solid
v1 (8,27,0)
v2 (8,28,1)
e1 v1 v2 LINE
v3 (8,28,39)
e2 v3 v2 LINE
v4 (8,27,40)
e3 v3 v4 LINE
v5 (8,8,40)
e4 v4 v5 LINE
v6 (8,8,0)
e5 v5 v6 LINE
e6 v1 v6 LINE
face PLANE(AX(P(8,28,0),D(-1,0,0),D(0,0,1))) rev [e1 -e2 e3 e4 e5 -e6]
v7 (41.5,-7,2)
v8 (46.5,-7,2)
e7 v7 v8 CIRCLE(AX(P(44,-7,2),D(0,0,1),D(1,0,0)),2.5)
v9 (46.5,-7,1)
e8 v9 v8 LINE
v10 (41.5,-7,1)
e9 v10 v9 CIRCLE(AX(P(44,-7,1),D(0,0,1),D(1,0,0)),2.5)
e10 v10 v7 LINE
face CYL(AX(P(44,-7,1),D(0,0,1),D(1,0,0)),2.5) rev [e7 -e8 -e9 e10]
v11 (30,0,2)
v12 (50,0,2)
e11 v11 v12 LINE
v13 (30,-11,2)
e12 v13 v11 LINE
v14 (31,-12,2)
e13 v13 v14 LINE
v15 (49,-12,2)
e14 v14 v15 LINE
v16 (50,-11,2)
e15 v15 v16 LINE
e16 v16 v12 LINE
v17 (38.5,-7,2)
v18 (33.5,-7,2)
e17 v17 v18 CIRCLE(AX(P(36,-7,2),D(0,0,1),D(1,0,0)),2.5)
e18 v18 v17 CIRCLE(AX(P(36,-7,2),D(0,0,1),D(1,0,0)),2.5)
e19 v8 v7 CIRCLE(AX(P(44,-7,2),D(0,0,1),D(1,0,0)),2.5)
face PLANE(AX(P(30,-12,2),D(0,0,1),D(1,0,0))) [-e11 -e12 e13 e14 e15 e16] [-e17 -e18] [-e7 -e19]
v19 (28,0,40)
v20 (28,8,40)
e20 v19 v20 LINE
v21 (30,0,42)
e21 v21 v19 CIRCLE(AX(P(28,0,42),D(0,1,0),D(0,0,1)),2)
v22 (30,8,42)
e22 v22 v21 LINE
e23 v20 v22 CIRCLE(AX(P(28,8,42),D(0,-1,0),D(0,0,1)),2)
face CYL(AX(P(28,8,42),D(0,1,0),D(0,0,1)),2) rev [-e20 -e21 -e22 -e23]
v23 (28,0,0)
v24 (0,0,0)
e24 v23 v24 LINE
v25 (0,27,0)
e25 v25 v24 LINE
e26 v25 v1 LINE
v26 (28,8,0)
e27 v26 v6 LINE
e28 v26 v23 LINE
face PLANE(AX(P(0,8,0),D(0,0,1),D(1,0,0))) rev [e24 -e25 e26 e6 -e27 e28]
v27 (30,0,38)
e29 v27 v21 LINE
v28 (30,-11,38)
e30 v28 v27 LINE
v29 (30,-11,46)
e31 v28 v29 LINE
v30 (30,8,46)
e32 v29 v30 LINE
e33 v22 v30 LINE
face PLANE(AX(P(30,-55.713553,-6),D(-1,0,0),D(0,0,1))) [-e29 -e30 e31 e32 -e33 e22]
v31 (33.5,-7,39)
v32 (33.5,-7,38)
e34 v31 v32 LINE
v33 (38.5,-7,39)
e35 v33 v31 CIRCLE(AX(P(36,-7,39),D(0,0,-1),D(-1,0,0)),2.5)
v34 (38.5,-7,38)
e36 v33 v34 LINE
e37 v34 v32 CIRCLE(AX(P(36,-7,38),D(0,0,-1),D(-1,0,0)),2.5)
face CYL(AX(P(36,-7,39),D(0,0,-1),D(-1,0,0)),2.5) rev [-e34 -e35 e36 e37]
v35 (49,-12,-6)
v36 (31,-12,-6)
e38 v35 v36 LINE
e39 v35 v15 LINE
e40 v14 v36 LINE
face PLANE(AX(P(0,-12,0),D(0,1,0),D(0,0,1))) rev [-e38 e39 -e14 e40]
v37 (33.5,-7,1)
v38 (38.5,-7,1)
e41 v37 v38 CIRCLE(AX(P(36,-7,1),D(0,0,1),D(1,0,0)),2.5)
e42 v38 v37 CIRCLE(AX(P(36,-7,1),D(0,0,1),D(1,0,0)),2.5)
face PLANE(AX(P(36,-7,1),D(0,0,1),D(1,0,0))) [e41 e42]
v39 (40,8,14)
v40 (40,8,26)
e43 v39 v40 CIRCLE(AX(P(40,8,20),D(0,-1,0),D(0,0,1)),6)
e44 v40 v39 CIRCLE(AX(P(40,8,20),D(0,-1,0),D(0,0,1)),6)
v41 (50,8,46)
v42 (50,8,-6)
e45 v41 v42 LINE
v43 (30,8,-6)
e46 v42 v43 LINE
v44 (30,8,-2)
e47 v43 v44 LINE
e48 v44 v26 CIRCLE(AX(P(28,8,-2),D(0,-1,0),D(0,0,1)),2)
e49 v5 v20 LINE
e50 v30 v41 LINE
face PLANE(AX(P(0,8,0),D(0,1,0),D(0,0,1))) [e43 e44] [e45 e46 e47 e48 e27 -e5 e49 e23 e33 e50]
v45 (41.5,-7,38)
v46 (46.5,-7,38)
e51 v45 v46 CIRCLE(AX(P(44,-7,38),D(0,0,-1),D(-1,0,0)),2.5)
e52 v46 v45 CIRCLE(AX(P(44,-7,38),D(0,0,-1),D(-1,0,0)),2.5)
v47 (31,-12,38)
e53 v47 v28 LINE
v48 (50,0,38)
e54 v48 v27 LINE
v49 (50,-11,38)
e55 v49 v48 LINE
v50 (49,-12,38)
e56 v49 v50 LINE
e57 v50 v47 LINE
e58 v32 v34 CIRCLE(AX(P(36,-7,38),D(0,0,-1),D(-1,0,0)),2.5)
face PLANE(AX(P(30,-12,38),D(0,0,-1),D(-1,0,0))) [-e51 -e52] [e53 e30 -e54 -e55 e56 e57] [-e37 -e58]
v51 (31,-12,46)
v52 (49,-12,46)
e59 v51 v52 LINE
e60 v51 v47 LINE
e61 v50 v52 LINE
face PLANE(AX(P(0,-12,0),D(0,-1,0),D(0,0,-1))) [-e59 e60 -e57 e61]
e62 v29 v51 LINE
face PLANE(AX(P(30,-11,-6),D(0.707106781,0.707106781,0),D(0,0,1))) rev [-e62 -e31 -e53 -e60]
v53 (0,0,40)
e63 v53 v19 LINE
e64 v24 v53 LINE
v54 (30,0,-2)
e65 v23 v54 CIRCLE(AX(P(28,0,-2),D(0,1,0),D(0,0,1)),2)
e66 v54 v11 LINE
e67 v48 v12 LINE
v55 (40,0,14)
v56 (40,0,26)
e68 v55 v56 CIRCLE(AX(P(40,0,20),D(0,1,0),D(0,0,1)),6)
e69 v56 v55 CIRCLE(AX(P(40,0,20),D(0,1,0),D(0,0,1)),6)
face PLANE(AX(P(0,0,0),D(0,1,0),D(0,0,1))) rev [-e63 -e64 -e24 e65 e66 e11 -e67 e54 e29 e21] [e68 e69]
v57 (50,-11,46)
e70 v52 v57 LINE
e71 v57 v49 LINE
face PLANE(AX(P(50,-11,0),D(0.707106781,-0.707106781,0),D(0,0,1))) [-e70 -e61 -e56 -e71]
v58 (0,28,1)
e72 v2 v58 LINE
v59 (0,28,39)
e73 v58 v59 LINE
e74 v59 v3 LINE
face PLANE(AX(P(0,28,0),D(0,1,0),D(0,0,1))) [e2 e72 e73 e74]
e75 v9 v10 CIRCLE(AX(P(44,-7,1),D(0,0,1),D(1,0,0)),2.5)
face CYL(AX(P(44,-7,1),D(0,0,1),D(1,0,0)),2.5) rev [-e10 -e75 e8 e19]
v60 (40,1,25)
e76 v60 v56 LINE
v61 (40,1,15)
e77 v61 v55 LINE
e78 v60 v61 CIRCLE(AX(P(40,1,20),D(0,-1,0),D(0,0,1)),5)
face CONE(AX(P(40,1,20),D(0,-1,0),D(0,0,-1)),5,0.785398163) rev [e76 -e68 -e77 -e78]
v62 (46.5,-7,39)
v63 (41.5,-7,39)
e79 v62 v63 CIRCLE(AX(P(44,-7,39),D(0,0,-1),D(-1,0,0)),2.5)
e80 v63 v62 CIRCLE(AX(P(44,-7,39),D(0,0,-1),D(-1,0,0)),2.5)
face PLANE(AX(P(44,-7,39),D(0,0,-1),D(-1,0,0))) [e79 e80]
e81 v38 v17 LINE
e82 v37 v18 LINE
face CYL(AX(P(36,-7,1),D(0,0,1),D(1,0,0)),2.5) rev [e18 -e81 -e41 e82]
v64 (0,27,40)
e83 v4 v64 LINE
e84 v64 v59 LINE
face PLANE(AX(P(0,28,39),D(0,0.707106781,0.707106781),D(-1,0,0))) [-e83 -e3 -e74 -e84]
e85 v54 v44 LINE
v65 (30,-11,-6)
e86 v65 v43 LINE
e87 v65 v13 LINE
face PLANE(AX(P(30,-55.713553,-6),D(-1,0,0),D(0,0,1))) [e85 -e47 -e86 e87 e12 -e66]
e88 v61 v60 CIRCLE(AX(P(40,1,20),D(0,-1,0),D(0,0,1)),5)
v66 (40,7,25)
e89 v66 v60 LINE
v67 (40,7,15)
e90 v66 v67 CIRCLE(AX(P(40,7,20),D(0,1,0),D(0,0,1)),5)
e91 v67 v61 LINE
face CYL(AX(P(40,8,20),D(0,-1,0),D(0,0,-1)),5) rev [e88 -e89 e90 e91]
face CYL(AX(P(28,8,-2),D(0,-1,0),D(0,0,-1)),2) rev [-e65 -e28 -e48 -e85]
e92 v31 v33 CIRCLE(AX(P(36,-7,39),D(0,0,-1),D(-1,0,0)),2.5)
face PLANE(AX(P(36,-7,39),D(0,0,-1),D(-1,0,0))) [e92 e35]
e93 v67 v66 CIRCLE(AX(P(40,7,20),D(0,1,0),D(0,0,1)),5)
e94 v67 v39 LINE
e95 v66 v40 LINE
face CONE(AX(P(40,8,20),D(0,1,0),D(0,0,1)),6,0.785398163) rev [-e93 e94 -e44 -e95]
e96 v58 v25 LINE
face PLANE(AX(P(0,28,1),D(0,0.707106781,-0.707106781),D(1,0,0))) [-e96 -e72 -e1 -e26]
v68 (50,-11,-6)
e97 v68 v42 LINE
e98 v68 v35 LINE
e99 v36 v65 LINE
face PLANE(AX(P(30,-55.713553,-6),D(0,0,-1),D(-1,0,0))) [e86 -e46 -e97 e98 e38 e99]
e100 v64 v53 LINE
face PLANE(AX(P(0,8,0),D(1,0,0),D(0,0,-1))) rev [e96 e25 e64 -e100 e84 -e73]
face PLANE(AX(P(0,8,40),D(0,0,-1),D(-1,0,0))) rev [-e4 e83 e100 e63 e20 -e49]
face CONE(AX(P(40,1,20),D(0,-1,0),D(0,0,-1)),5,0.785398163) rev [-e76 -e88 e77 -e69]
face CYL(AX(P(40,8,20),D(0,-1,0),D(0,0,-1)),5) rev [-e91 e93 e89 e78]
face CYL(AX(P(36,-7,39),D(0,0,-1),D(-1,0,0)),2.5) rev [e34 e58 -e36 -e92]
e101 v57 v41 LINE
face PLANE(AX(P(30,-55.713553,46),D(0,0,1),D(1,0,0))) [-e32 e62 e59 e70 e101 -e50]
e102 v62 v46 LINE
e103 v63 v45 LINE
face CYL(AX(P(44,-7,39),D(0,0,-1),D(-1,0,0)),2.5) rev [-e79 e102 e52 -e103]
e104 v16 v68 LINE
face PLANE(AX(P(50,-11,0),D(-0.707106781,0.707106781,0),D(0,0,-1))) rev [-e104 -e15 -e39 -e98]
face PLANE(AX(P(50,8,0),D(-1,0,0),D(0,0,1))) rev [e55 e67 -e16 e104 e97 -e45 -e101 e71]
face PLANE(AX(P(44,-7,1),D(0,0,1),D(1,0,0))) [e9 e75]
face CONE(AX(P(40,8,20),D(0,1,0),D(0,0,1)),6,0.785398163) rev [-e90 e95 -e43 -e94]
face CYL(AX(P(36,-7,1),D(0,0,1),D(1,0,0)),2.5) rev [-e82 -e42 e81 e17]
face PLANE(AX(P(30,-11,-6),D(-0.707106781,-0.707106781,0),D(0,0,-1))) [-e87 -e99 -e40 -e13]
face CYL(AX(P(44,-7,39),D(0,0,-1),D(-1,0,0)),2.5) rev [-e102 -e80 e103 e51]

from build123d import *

# Parameters (mm, degrees)
SKETCH1_W           = 50
SKETCH1_H           = 40
BOSS_EXTRUDE1_DEPTH = 8
SKETCH3_W           = 20
SKETCH3_H           = 52
BOSS_EXTRUDE2_DEPTH = 8
SKETCH2_R           = 5
CUT_EXTRUDE1_DEPTH  = 69.410525506
CHAMFER2_SIZE       = 1
SKETCH4_W           = 20
SKETCH4_H           = 8
BOSS_EXTRUDE3_DEPTH = 12
CHAMFER4_SIZE       = 1
FILLET1_R           = 2
SKETCH5_W           = 8
SKETCH5_H           = 40
BOSS_EXTRUDE4_DEPTH = 20
CHAMFER5_SIZE       = 1
SKETCH6_R           = 2.5
CUT_EXTRUDE2_DEPTH  = 1
CUT_EXTRUDE3_START  = -1
SKETCH7_R           = 2.5
CUT_EXTRUDE3_DEPTH  = 1


with BuildPart() as part:
    # Sketch1 → Boss-Extrude1 (new body)
    with BuildSketch(Plane(origin=(0, 0, 0), x_dir=(1, 0, 0), z_dir=(0, 1, 0))):
        with Locations((25, -20)):
            Rectangle(SKETCH1_W, SKETCH1_H)
    extrude(amount=BOSS_EXTRUDE1_DEPTH)

    # Sketch3 → Boss-Extrude2 (add)
    with BuildSketch(Plane(origin=(0, 8, 0), x_dir=(1, 0, 0), z_dir=(0, 1, 0))):
        with Locations((40, -20)):
            Rectangle(SKETCH3_W, SKETCH3_H)
    extrude(amount=-BOSS_EXTRUDE2_DEPTH)

    # Sketch2 → Cut-Extrude1 (cut, through all)
    with BuildSketch(Plane.XZ):
        with Locations(Location((40, 20, 0), (0, 0, 270))):
            Circle(SKETCH2_R)
    extrude(amount=-CUT_EXTRUDE1_DEPTH, mode=Mode.SUBTRACT)

    # Chamfer2
    chamfer2_edges = [part.edges().sort_by_distance(p)[0] for p in [
        (40, 8, 25),
        (40, 0, 25),
    ]]
    chamfer(chamfer2_edges, length=CHAMFER2_SIZE)

    # Sketch4 → Boss-Extrude3 (add)
    with BuildSketch(Plane(origin=(0, 0, 0), x_dir=(1, 0, 0), z_dir=(0, 1, 0))):
        with Locations((40, -42)):
            Rectangle(SKETCH4_W, SKETCH4_H)
        with Locations((40, 2)):
            Rectangle(SKETCH4_W, SKETCH4_H)
    extrude(amount=-BOSS_EXTRUDE3_DEPTH)

    # Chamfer4
    chamfer4_edges = [part.edges().sort_by_distance(p)[0] for p in [
        (30, -12, 42),
        (50, -12, 42),
        (30, -12, -2),
        (50, -12, -2),
    ]]
    chamfer(chamfer4_edges, length=CHAMFER4_SIZE)

    # Fillet1
    fillet1_edges = [part.edges().sort_by_distance(p)[0] for p in [
        (30, 4, 40),
        (30, 4, 0),
    ]]
    fillet(fillet1_edges, radius=FILLET1_R)

    # Sketch5 → Boss-Extrude4 (add)
    with BuildSketch(Plane(origin=(0, 8, 0), x_dir=(1, 0, 0), z_dir=(0, 1, 0))):
        with Locations((4, -20)):
            Rectangle(SKETCH5_W, SKETCH5_H)
    extrude(amount=BOSS_EXTRUDE4_DEPTH)

    # Chamfer5
    chamfer5_edges = [part.edges().sort_by_distance(p)[0] for p in [
        (4, 28, 40),
        (4, 28, 0),
    ]]
    chamfer(chamfer5_edges, length=CHAMFER5_SIZE)

    # Sketch6 → Cut-Extrude2 (cut)
    with BuildSketch(Plane.XY.offset(2)):
        with Locations((44, -7)):
            Circle(SKETCH6_R)
        with Locations((36, -7)):
            Circle(SKETCH6_R)
    extrude(amount=-CUT_EXTRUDE2_DEPTH, mode=Mode.SUBTRACT)

    # Sketch7 → Cut-Extrude3 (cut)
    with BuildSketch(Plane(origin=(0, 0, 38), x_dir=(-1, 0, 0), z_dir=(0, 0, -1)).offset(CUT_EXTRUDE3_START)):
        with Locations(Location((-36, -7, 0), (0, 0, 180))):
            Circle(SKETCH7_R)
        with Locations(Location((-44, -7, 0), (0, 0, 180))):
            Circle(SKETCH7_R)
    extrude(amount=CUT_EXTRUDE3_DEPTH, mode=Mode.SUBTRACT)


solid = part.part
